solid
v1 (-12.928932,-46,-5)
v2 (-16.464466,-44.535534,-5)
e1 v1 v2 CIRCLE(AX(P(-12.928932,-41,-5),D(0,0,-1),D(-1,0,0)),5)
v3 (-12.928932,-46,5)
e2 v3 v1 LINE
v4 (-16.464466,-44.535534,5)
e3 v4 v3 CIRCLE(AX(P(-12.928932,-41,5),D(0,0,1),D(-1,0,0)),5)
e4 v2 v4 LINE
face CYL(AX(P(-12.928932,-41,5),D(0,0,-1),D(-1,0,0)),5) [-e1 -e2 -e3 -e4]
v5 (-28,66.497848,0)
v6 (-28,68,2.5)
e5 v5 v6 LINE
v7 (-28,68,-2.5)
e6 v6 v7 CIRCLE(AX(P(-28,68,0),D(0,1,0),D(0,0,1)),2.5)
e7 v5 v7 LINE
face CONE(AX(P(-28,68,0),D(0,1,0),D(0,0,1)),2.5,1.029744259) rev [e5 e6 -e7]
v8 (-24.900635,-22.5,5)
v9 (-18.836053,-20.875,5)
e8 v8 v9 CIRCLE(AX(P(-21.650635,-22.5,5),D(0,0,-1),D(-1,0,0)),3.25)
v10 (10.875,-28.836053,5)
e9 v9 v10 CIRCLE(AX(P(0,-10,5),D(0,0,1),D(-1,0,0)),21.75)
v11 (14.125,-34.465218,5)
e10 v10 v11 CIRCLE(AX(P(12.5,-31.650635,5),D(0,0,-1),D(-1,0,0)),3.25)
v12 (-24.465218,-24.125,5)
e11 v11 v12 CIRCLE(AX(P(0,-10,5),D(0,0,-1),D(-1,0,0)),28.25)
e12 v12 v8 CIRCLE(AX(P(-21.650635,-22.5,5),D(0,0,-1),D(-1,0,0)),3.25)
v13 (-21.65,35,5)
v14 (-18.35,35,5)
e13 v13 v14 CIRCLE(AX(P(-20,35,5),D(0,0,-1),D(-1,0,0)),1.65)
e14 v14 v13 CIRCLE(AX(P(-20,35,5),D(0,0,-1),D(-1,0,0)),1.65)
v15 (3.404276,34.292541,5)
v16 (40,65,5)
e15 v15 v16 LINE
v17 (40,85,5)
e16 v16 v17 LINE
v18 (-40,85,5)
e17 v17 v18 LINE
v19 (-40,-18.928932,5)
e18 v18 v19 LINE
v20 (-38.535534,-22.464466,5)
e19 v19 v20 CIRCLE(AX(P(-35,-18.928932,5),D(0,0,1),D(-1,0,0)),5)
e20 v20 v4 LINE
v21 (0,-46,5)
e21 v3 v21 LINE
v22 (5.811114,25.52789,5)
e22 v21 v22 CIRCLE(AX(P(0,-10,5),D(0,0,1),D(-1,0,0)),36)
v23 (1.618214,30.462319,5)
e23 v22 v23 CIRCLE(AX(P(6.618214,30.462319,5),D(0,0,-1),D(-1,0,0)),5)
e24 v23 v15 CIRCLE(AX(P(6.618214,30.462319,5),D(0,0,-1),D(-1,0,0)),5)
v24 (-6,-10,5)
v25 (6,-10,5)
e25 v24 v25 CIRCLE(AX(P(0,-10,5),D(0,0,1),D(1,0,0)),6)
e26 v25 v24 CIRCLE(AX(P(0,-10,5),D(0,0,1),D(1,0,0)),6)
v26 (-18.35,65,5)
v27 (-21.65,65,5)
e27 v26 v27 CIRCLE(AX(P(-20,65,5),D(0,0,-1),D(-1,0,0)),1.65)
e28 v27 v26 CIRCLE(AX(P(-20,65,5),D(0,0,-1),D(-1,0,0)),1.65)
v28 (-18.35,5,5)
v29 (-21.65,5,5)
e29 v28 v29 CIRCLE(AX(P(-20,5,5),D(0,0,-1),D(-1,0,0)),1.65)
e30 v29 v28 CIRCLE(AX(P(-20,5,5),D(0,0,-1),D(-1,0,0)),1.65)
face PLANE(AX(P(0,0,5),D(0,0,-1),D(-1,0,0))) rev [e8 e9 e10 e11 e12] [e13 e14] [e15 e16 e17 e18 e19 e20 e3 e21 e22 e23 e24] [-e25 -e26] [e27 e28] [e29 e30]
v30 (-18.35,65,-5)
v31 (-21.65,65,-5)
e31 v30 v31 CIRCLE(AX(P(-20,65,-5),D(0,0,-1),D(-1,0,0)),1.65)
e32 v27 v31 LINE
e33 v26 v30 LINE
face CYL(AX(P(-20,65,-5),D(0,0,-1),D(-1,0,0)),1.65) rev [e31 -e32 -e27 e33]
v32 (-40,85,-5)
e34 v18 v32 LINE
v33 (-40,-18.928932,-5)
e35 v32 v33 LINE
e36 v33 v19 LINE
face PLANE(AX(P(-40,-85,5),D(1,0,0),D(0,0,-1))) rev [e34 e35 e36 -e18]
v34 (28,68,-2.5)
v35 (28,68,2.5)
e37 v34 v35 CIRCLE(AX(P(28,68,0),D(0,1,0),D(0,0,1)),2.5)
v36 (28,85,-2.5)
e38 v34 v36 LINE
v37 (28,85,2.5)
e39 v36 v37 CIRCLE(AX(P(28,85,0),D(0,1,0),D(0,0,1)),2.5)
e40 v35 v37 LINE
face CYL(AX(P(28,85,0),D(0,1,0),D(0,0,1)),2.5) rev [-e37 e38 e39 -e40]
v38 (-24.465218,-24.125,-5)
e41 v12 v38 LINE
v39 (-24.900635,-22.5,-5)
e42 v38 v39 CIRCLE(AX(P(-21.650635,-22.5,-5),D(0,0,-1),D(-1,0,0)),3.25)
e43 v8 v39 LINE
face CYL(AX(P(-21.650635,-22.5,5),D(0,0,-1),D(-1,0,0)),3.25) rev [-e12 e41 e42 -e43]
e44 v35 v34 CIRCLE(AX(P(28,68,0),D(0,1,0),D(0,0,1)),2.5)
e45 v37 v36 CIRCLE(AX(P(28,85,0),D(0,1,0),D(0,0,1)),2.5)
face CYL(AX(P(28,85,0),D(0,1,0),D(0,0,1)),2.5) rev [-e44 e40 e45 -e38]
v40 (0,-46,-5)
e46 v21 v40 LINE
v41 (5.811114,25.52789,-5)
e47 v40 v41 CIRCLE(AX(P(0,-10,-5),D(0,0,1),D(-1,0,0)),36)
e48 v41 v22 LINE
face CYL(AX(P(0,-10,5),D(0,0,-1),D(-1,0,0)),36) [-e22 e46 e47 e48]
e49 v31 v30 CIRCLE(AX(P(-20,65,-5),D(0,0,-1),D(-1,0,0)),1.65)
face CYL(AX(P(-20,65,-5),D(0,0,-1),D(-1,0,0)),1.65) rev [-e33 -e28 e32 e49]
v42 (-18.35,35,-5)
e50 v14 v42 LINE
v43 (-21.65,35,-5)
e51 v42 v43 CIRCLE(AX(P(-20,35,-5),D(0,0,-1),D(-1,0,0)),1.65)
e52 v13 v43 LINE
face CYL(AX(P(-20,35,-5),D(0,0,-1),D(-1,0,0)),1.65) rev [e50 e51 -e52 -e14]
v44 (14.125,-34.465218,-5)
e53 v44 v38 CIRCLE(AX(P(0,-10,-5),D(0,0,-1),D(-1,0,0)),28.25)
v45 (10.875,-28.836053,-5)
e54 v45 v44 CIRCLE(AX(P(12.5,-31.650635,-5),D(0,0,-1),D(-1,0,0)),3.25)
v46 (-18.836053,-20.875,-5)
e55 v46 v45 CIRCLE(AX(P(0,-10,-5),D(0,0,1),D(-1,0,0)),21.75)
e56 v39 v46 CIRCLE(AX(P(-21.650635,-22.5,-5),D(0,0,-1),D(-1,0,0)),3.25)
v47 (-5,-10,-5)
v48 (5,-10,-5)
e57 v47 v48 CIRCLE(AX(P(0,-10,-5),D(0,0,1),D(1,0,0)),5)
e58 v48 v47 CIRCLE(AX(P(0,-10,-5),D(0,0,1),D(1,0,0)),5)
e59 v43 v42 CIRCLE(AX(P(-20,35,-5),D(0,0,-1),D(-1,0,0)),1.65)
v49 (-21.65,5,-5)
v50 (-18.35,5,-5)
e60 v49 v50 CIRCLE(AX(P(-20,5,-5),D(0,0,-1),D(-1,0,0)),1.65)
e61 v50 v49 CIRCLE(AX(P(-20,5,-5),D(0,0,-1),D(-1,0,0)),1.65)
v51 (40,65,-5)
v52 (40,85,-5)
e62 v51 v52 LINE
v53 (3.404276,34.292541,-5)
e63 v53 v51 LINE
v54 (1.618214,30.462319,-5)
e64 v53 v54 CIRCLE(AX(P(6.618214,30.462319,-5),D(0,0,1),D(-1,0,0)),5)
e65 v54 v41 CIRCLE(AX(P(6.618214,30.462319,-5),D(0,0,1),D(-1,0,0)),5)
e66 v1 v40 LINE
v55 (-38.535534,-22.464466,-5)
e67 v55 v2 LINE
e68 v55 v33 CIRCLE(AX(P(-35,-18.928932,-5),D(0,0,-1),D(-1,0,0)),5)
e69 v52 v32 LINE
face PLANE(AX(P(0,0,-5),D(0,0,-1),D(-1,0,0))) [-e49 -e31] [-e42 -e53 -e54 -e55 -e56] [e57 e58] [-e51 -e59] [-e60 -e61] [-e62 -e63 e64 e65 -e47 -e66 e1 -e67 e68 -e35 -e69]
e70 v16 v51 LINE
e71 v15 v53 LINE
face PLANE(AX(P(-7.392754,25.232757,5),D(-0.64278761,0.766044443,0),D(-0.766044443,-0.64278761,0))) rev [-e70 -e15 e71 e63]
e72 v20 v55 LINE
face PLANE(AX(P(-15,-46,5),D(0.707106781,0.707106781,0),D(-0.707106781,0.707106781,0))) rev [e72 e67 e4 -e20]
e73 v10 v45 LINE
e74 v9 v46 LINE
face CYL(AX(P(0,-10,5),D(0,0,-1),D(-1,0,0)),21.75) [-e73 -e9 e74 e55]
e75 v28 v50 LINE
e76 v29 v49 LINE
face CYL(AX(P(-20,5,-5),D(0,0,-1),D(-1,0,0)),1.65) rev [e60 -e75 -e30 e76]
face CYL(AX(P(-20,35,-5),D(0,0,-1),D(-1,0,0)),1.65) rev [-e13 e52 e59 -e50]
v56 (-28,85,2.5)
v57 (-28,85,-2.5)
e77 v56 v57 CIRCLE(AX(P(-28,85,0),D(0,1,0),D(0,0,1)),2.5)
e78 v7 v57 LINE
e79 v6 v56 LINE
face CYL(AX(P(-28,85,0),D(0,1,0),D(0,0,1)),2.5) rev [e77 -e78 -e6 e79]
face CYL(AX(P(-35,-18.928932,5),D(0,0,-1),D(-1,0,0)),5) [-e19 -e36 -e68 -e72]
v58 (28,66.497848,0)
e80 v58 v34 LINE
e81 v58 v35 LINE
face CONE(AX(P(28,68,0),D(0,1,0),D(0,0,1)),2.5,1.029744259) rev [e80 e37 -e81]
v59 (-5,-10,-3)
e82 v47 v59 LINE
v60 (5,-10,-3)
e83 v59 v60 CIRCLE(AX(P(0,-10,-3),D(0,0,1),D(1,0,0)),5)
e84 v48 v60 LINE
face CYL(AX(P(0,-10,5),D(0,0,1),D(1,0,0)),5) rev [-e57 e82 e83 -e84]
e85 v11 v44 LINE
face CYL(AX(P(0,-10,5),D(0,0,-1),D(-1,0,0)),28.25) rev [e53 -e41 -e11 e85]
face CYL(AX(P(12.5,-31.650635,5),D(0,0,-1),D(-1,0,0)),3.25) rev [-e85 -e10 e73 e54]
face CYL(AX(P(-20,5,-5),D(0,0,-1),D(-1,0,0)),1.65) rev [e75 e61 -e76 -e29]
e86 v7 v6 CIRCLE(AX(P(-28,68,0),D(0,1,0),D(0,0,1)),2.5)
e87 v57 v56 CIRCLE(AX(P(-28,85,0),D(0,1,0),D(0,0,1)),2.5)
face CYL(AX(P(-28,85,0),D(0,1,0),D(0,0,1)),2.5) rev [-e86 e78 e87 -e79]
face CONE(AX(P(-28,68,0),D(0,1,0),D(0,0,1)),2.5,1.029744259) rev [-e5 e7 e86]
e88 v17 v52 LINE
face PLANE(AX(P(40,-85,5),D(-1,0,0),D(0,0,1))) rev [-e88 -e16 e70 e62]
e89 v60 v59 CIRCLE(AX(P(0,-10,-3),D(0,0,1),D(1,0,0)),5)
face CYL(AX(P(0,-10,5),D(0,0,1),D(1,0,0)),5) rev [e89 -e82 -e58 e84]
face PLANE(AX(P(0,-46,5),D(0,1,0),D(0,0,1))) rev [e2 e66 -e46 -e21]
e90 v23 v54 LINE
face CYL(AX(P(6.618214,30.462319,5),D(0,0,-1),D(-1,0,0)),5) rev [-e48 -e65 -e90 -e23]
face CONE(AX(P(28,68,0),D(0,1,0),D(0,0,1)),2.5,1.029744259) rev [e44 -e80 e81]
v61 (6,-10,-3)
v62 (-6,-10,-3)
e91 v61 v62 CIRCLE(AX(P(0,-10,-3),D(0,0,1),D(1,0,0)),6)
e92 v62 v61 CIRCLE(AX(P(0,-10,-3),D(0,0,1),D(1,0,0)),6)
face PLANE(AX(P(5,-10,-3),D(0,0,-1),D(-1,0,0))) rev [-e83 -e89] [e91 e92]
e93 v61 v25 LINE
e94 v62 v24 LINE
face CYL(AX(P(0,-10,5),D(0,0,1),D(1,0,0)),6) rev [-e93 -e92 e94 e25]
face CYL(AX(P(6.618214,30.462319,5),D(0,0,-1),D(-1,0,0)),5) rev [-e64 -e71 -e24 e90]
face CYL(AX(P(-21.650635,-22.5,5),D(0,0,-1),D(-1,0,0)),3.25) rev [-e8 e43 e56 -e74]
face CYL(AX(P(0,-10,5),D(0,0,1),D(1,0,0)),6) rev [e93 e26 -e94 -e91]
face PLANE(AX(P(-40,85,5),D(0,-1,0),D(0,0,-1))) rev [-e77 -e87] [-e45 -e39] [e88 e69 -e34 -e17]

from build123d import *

# Parameters (mm, degrees)
SKETCH_1_W                = 80
SKETCH_1_H                = 170
EXTRUDE_1_DEPTH           = 5
HOLE_WIZARD_1_D           = 10
HOLE_WIZARD_1_CBORE_D     = 12
HOLE_WIZARD_1_CBORE_DEPTH = 8
CUT_EXTRUDE_2_DEPTH       = 95.472218138
CUT_EXTRUDE_4_DEPTH       = 95.472218138
FILLET_1_R                = 5
HOLE_WIZARD_M6_1_D        = 5
HOLE_WIZARD_M6_1_DEPTH    = 17
HOLE_WIZARD_M6_1_TIP      = 1.502151548
HOLE_WIZARD_M4_1_D        = 3.3


with BuildPart() as part:
    # 草图1 → 凸台-拉伸1 (new, symmetric)
    with BuildSketch(Plane.XY):
        Rectangle(SKETCH_1_W, SKETCH_1_H)
    extrude(amount=EXTRUDE_1_DEPTH, both=True)

    # 孔1 (through all)
    with Locations(Plane(origin=(0, 0, 5), x_dir=(-1, 0, 0), z_dir=(0, 0, 1))):
        with Locations((0, 10)):
            CounterBoreHole(HOLE_WIZARD_1_D / 2, HOLE_WIZARD_1_CBORE_D / 2, HOLE_WIZARD_1_CBORE_DEPTH)

    # 草图6 → 切除-拉伸2 (cut, through all)
    with BuildSketch(Plane(origin=(0, 0, -5), x_dir=(-1, 0, 0), z_dir=(0, 0, -1))):
        with BuildLine():
            ThreePointArc((-14.125, -34.465217657), (7.311638024, -37.287404593), (24.465217657, -24.125))
            ThreePointArc((24.465217657, -24.125), (23.275635095, -19.685417438), (18.836052532, -20.875))
            ThreePointArc((18.836052532, -20.875), (5.629314231, -31.008886722), (-10.875, -28.836052532))
            ThreePointArc((-10.875, -28.836052532), (-15.314582562, -30.025635095), (-14.125, -34.465217657))
        make_face()
    extrude(amount=-CUT_EXTRUDE_2_DEPTH, mode=Mode.SUBTRACT)

    # 草图11 → 切除-拉伸4 (cut, through all)
    with BuildSketch(Plane(origin=(0, 0, -5), x_dir=(-1, 0, 0), z_dir=(0, 0, -1))):
        with BuildLine():
            Line((0, -46), (15, -46))
            Line((15, -46), (40, -21))
            Line((40, -21), (40, -85))
            Line((40, -85), (-40, -85))
            Line((-40, -85), (-40, 65))
            Line((-40, 65), (7.392754444, 25.232757226))
            ThreePointArc((7.392754444, 25.232757226), (-35.807675575, -6.283769392), (0, -46))
        make_face()
    extrude(amount=-CUT_EXTRUDE_4_DEPTH, mode=Mode.SUBTRACT)

    # 圆角1
    fillet_1_edges = [part.edges().sort_by_distance(p)[0] for p in [
        (-40, -21, 0),
        (-7.392754444, 25.232757226, 0),
        (-15, -46, 0),
    ]]
    fillet(fillet_1_edges, radius=FILLET_1_R)

    # M6 螺纹孔1
    with Locations(Plane(origin=(0, 85, 0), x_dir=(1, 0, 0), z_dir=(0, 1, 0))):
        with Locations((-28, 0), (28, 0)):
            Hole(HOLE_WIZARD_M6_1_D / 2, depth=HOLE_WIZARD_M6_1_DEPTH)
            with Locations((0, 0, -(HOLE_WIZARD_M6_1_DEPTH + HOLE_WIZARD_M6_1_TIP / 2))):  # 118° drill point
                Cone(0, HOLE_WIZARD_M6_1_D / 2, HOLE_WIZARD_M6_1_TIP, mode=Mode.SUBTRACT)

    # M4 螺纹孔1 (through all)
    with Locations(Plane(origin=(0, 0, -5), x_dir=(-1, 0, 0), z_dir=(0, 0, -1))):
        with Locations((20, 35), (20, 65), (20, 5)):
            Hole(HOLE_WIZARD_M4_1_D / 2)


solid = part.part
